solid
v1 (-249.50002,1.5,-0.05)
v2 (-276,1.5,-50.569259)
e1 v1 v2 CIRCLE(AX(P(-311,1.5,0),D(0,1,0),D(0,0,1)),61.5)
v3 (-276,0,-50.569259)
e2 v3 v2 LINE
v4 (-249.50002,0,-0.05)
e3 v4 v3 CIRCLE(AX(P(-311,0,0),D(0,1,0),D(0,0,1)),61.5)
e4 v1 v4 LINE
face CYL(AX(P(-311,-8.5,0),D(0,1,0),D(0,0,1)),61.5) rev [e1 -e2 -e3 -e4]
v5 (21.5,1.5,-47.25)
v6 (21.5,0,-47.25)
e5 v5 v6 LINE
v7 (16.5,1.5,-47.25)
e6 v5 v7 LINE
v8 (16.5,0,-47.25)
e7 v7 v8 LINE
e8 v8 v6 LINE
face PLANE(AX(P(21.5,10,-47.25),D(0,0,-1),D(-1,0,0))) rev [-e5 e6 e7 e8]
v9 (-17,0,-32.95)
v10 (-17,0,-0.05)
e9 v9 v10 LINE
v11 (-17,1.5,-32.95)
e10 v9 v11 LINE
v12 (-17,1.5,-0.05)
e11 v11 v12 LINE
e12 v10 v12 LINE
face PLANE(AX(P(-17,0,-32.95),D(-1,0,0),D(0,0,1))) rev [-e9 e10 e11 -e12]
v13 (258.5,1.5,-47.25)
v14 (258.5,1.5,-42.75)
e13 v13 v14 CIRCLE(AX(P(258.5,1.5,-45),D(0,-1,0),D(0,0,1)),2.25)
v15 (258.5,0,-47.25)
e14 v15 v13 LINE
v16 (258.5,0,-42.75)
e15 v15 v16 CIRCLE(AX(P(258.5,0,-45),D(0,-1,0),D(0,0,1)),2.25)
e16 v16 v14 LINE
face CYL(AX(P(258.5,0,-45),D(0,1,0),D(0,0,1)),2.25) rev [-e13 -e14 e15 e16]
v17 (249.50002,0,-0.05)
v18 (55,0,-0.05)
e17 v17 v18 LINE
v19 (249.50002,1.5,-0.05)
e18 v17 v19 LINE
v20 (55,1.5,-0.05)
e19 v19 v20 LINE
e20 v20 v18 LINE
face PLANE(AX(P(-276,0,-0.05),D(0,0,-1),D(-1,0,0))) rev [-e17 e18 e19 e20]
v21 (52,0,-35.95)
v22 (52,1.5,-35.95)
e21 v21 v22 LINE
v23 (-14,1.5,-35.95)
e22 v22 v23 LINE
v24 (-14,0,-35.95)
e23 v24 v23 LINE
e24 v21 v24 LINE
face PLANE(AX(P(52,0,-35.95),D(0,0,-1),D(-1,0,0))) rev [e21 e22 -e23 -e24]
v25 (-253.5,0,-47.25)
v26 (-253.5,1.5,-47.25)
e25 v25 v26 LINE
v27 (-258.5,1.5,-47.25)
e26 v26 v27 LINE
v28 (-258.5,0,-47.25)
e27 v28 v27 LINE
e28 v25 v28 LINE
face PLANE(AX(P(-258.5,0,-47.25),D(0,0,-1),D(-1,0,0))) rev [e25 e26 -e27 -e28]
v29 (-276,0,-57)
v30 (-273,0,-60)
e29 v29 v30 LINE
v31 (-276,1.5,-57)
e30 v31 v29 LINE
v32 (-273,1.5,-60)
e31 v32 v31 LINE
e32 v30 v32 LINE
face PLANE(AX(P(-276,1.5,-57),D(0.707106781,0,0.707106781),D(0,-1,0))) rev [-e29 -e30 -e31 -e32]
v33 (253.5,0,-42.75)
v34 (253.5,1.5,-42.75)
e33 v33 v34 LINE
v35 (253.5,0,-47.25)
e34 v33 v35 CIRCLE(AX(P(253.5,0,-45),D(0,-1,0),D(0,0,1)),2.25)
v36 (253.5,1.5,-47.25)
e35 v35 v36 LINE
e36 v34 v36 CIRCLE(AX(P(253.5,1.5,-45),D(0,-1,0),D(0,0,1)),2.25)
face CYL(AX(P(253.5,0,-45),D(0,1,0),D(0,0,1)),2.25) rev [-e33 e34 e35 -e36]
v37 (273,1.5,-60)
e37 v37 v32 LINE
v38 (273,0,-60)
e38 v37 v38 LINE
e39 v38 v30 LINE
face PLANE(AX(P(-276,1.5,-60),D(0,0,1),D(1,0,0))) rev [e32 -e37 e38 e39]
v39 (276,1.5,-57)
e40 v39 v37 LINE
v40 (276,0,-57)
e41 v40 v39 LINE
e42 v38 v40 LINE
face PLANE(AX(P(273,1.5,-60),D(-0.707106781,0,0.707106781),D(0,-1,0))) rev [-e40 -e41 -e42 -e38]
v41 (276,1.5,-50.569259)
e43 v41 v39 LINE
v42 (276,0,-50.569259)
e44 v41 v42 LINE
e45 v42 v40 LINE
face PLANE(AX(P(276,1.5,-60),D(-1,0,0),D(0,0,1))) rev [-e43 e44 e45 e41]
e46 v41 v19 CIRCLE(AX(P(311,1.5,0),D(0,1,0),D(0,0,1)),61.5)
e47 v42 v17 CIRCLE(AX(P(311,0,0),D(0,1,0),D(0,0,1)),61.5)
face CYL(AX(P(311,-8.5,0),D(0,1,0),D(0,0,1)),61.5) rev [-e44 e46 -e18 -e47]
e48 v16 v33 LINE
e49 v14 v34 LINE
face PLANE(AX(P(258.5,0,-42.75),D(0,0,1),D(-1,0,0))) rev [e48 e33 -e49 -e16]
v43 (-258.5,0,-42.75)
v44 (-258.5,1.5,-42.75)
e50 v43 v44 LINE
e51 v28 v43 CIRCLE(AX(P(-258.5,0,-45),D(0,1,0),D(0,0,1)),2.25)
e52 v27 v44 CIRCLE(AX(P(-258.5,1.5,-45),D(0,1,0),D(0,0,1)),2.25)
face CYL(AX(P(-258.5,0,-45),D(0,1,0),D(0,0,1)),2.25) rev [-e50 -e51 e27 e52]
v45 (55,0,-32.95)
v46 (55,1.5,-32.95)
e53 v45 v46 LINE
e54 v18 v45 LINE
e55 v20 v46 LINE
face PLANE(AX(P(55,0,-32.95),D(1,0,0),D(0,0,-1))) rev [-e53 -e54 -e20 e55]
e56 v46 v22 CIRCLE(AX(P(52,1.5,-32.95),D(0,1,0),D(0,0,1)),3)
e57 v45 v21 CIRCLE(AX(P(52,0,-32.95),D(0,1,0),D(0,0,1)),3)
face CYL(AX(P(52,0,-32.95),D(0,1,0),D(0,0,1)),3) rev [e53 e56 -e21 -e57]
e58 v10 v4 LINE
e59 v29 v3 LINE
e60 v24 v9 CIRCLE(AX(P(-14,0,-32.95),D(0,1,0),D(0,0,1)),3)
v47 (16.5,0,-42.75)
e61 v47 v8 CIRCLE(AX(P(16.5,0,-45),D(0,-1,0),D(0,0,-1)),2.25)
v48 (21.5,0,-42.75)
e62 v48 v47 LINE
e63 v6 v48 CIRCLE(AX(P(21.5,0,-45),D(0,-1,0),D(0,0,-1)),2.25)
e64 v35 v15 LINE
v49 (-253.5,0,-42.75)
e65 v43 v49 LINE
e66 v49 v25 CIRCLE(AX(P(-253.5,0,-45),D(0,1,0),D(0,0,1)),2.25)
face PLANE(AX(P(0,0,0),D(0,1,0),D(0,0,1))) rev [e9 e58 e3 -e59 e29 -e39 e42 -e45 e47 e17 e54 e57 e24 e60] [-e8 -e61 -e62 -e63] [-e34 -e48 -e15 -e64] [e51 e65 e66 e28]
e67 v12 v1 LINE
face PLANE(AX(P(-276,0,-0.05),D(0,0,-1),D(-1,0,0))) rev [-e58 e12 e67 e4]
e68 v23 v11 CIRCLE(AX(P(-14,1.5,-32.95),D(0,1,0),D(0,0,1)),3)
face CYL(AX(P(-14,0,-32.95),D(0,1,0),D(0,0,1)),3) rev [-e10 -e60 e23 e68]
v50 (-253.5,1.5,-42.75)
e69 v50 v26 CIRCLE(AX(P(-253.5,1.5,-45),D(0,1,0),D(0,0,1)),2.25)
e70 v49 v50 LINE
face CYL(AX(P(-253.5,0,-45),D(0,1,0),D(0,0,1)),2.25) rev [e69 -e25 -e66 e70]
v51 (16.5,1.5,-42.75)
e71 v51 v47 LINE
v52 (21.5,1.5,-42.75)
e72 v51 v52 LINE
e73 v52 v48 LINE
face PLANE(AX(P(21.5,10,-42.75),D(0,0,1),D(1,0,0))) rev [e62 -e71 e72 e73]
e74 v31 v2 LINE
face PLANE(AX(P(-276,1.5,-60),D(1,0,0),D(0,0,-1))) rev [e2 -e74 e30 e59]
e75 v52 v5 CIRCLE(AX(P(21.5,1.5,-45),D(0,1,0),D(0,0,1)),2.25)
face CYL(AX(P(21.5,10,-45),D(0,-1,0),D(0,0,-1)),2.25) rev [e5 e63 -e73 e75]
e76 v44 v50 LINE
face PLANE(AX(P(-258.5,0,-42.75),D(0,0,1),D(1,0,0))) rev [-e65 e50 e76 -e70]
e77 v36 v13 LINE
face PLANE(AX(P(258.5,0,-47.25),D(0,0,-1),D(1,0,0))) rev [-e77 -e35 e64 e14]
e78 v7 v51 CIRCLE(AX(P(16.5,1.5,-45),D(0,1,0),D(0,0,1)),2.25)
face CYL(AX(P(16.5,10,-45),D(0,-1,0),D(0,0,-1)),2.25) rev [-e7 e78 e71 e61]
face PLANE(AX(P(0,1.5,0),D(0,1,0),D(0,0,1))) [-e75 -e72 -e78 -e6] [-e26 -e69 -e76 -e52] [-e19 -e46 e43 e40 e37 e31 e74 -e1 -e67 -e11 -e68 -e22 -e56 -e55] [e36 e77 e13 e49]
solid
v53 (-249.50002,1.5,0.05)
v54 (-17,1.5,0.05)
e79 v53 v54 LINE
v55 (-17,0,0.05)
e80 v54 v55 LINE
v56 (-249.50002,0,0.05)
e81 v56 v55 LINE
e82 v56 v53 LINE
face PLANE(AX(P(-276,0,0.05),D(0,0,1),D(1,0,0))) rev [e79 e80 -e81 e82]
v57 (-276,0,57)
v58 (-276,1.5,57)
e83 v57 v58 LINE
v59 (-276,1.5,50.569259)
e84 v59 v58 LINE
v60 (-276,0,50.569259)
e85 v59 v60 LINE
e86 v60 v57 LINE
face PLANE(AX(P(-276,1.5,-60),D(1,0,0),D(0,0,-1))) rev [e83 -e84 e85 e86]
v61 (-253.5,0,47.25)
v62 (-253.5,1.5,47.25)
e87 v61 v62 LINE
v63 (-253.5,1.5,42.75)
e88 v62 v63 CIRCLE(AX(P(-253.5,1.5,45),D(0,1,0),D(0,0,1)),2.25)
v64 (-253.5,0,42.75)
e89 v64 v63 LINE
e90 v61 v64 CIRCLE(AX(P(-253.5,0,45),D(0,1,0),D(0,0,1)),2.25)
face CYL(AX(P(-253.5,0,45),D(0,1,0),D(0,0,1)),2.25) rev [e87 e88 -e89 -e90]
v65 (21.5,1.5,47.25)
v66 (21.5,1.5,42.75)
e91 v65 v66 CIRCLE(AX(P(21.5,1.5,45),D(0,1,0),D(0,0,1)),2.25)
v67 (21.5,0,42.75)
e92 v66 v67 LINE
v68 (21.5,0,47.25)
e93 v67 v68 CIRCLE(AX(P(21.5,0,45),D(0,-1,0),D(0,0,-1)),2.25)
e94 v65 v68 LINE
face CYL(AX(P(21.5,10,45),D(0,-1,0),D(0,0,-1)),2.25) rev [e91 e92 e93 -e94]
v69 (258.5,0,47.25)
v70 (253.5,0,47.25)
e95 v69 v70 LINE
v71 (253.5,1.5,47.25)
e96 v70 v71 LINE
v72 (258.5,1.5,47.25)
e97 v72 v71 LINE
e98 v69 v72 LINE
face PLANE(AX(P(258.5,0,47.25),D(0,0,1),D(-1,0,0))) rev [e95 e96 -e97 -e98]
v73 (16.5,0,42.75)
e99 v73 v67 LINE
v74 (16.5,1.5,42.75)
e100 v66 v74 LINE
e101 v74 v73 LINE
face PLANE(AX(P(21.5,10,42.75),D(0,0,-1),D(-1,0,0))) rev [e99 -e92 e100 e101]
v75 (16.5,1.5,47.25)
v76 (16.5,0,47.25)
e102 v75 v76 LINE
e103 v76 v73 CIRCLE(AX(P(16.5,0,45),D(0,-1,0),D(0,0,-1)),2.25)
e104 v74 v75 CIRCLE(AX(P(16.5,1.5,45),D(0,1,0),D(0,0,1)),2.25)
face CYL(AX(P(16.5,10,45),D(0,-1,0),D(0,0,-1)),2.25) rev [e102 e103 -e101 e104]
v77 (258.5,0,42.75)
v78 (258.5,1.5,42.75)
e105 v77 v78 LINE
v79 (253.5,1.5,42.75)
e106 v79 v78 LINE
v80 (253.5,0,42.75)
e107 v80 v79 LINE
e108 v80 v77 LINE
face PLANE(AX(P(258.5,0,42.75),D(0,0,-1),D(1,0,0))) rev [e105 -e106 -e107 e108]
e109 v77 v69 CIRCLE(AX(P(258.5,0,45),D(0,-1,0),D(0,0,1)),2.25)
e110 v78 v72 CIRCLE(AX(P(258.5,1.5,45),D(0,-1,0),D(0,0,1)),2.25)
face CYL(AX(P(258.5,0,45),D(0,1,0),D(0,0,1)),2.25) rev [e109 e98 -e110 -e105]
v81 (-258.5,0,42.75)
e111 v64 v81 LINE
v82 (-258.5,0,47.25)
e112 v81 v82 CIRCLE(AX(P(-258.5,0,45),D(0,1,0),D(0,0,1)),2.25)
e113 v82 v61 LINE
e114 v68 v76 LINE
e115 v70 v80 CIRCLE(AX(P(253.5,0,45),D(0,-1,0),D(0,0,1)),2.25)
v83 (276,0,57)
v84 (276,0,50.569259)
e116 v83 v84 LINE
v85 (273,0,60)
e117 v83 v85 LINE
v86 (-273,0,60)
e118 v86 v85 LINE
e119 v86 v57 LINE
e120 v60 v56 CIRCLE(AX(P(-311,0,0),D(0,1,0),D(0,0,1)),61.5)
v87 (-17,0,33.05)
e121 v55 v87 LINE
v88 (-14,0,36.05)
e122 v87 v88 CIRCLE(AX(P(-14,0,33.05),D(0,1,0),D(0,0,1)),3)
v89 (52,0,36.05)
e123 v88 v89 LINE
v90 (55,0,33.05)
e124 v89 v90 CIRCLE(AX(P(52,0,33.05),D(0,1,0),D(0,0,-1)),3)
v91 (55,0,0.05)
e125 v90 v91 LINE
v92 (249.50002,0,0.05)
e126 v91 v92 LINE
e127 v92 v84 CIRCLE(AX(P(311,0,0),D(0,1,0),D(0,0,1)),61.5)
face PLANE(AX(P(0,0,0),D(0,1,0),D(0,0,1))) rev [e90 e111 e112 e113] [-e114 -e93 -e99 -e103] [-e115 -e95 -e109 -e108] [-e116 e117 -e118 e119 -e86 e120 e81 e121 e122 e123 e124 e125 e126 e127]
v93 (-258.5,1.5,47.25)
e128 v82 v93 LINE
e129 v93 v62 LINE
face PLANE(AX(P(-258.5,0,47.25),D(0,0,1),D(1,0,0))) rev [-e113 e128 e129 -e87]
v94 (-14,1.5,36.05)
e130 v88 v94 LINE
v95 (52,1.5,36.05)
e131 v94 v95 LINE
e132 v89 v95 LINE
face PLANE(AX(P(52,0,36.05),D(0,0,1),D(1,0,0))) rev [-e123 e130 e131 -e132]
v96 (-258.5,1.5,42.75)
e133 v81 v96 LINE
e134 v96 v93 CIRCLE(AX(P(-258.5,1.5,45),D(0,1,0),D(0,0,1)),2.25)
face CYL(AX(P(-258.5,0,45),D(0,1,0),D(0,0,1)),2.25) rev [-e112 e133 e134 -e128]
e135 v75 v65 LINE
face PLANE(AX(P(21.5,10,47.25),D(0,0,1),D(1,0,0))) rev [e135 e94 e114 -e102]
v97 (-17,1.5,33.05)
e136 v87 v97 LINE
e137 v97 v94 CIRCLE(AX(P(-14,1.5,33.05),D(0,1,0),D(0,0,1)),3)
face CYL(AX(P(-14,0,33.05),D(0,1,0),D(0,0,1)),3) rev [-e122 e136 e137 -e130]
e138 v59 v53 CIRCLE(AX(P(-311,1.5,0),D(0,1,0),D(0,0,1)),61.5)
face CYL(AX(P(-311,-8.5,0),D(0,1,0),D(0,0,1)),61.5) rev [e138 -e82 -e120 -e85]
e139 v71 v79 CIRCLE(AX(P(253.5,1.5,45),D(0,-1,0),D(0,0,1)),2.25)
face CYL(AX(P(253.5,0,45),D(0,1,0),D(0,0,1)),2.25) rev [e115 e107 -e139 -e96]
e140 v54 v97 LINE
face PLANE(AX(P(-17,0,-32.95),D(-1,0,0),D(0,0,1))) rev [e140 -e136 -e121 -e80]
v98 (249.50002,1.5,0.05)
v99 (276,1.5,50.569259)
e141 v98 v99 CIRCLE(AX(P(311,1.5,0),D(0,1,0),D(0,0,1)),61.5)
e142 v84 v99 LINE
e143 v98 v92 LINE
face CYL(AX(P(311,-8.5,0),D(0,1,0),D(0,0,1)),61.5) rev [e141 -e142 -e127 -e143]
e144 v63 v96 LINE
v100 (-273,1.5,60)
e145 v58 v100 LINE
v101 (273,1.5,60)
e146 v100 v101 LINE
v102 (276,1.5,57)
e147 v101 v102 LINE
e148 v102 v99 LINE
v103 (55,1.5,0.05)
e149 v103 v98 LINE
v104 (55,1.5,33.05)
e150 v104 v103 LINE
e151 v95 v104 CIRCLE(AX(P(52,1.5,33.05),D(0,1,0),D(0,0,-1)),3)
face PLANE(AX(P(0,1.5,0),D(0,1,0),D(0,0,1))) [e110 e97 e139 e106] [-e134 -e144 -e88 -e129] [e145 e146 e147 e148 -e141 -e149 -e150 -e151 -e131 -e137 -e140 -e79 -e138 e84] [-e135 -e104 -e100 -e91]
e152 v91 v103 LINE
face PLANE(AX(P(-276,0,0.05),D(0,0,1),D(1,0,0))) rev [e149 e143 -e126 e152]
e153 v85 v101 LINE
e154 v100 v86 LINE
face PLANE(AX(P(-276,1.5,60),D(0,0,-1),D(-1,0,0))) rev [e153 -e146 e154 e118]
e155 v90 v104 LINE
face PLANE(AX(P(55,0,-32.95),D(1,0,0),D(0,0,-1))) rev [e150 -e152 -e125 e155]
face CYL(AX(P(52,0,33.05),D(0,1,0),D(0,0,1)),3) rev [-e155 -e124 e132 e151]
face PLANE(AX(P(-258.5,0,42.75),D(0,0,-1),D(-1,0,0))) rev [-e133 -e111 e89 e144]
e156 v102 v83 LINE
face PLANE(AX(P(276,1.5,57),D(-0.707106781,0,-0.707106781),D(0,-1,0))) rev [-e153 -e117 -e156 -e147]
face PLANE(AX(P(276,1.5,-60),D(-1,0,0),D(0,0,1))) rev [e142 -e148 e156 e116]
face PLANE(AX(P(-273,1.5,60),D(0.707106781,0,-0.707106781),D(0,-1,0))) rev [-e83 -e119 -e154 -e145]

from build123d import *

# Parameters (mm, degrees)
SKETCH1_W           = 552
SKETCH1_H           = 120
BOSS_EXTRUDE1_DEPTH = 1.5
CHAMFER1_SIZE       = 3
CHAMFER2_SIZE       = 3
CUT_EXTRUDE6_DEPTH  = 283.45043813
SKETCH13_W          = 552
SKETCH13_H          = 0.1
CUT_EXTRUDE7_DEPTH  = 283.45043813
CUT_EXTRUDE9_DEPTH  = 283.45043813
SKETCH16_R          = 61.5
CUT_EXTRUDE10_DEPTH = 10
CUT_EXTRUDE11_DEPTH = 10


with BuildPart() as part:
    # Sketch1 → Boss-Extrude1 (new body)
    with BuildSketch(Plane(origin=(0, 0, 0), x_dir=(1, 0, 0), z_dir=(0, 1, 0))):
        Rectangle(SKETCH1_W, SKETCH1_H)
    extrude(amount=BOSS_EXTRUDE1_DEPTH)

    # Chamfer1
    chamfer1_edges = [part.edges().sort_by_distance(p)[0] for p in [
        (276, 0.75, 60),
        (276, 0.75, -60),
    ]]
    chamfer(chamfer1_edges, length=CHAMFER1_SIZE)

    # Chamfer2
    chamfer2_edges = [part.edges().sort_by_distance(p)[0] for p in [
        (-276, 0.75, 60),
        (-276, 0.75, -60),
    ]]
    chamfer(chamfer2_edges, length=CHAMFER2_SIZE)

    # Sketch12 → Cut-Extrude6 (cut, through all)
    with BuildSketch(Plane(origin=(0, 1.5, 0), x_dir=(1, 0, 0), z_dir=(0, 1, 0))):
        with BuildLine():
            Line((-258.5, 47.25), (-253.5, 47.25))
            ThreePointArc((-253.5, 47.25), (-251.25, 45), (-253.5, 42.75))
            Line((-253.5, 42.75), (-258.5, 42.75))
            ThreePointArc((-258.5, 42.75), (-260.75, 45), (-258.5, 47.25))
        make_face()
        with BuildLine():
            Line((-258.5, -42.75), (-253.5, -42.75))
            ThreePointArc((-253.5, -42.75), (-251.25, -45), (-253.5, -47.25))
            Line((-253.5, -47.25), (-258.5, -47.25))
            ThreePointArc((-258.5, -47.25), (-260.75, -45), (-258.5, -42.75))
        make_face()
    cut_extrude6 = extrude(amount=-CUT_EXTRUDE6_DEPTH, mode=Mode.SUBTRACT)

    # Sketch13 → Cut-Extrude7 (cut, through all)
    with BuildSketch(Plane(origin=(0, 1.5, 0), x_dir=(1, 0, 0), z_dir=(0, 1, 0))):
        Rectangle(SKETCH13_W, SKETCH13_H)
    extrude(amount=-CUT_EXTRUDE7_DEPTH, mode=Mode.SUBTRACT)


with BuildPart() as cut_extrude7_piece_1:
    # of the separate pieces the step leaves, piece 1, a body of its own (cut_extrude7_pieces)
    add(part.part.solids().sort_by_distance((-273, 0, -60))[0])


with BuildPart() as cut_extrude7_piece_2:
    # of the separate pieces the step leaves, piece 2, a body of its own (cut_extrude7_pieces)
    add(part.part.solids().sort_by_distance((-276, 0, 57))[0])


with BuildPart() as cut_extrude9_tool:
    # Sketch15 → Cut-Extrude9 (new, through all)
    with BuildSketch(Plane(origin=(0, 1.5, 0), x_dir=(1, 0, 0), z_dir=(0, 1, 0))):
        with BuildLine():
            Line((52, 35.95), (-14, 35.95))
            ThreePointArc((-14, 35.95), (-16.121320344, 35.071320344), (-17, 32.95))
            Line((-17, 32.95), (-17, -33.05))
            ThreePointArc((-17, -33.05), (-16.121320344, -35.171320344), (-14, -36.05))
            Line((-14, -36.05), (52, -36.05))
            ThreePointArc((52, -36.05), (54.121320344, -35.171320344), (55, -33.05))
            Line((55, -33.05), (55, 32.95))
            ThreePointArc((55, 32.95), (54.121320344, 35.071320344), (52, 35.95))
        make_face()
    extrude(amount=-CUT_EXTRUDE9_DEPTH)


with BuildPart() as cut_extrude7_piece_1_1:
    add(cut_extrude7_piece_1.part)

    # Cut-Extrude9: cut by cut_extrude9_tool
    add(cut_extrude9_tool.part, mode=Mode.SUBTRACT)


with BuildPart() as cut_extrude7_piece_2_1:
    add(cut_extrude7_piece_2.part)

    # Cut-Extrude9: cut by cut_extrude9_tool
    add(cut_extrude9_tool.part, mode=Mode.SUBTRACT)


with BuildPart() as cut_extrude10_tool:
    # Sketch16 → Cut-Extrude10 (new body)
    with BuildSketch(Plane(origin=(0, 1.5, 0), x_dir=(1, 0, 0), z_dir=(0, 1, 0))):
        with Locations((311, 0)):
            Circle(SKETCH16_R)
        with Locations((-311, 0)):
            Circle(SKETCH16_R)
    extrude(amount=-CUT_EXTRUDE10_DEPTH)


with BuildPart() as cut_extrude7_piece_1_2:
    add(cut_extrude7_piece_1_1.part)

    # Cut-Extrude10: cut by cut_extrude10_tool
    add(cut_extrude10_tool.part, mode=Mode.SUBTRACT)


with BuildPart() as cut_extrude7_piece_2_2:
    add(cut_extrude7_piece_2_1.part)

    # Cut-Extrude10: cut by cut_extrude10_tool
    add(cut_extrude10_tool.part, mode=Mode.SUBTRACT)


with BuildPart() as mirror1_tool:
    # Mirror1: Cut-Extrude6 across plane
    add(cut_extrude6.mirror(Plane(origin=(0, 0, 0), x_dir=(0, 0, 1), z_dir=(1, 0, 0))))


with BuildPart() as cut_extrude7_piece_1_3:
    add(cut_extrude7_piece_1_2.part)

    # Mirror1: cut by mirror1_tool
    add(mirror1_tool.part, mode=Mode.SUBTRACT)


with BuildPart() as cut_extrude7_piece_2_3:
    add(cut_extrude7_piece_2_2.part)

    # Mirror1: cut by mirror1_tool
    add(mirror1_tool.part, mode=Mode.SUBTRACT)


with BuildPart() as cut_extrude11_tool:
    # Sketch17 → Cut-Extrude11 (new body)
    with BuildSketch(Plane.XZ):
        with BuildLine():
            Line((21.5, -47.25), (16.5, -47.25))
            ThreePointArc((16.5, -47.25), (14.25, -45), (16.5, -42.75))
            Line((16.5, -42.75), (21.5, -42.75))
            ThreePointArc((21.5, -42.75), (23.75, -45), (21.5, -47.25))
        make_face()
        with BuildLine():
            Line((21.5, 42.75), (16.5, 42.75))
            ThreePointArc((16.5, 42.75), (14.25, 45), (16.5, 47.25))
            Line((16.5, 47.25), (21.5, 47.25))
            ThreePointArc((21.5, 47.25), (23.75, 45), (21.5, 42.75))
        make_face()
    extrude(amount=-CUT_EXTRUDE11_DEPTH)


with BuildPart() as cut_extrude7_piece_1_4:
    add(cut_extrude7_piece_1_3.part)

    # Cut-Extrude11: cut by cut_extrude11_tool
    add(cut_extrude11_tool.part, mode=Mode.SUBTRACT)


with BuildPart() as cut_extrude7_piece_2_4:
    add(cut_extrude7_piece_2_3.part)

    # Cut-Extrude11: cut by cut_extrude11_tool
    add(cut_extrude11_tool.part, mode=Mode.SUBTRACT)


solid = Compound([cut_extrude7_piece_1_4.part, cut_extrude7_piece_2_4.part])
